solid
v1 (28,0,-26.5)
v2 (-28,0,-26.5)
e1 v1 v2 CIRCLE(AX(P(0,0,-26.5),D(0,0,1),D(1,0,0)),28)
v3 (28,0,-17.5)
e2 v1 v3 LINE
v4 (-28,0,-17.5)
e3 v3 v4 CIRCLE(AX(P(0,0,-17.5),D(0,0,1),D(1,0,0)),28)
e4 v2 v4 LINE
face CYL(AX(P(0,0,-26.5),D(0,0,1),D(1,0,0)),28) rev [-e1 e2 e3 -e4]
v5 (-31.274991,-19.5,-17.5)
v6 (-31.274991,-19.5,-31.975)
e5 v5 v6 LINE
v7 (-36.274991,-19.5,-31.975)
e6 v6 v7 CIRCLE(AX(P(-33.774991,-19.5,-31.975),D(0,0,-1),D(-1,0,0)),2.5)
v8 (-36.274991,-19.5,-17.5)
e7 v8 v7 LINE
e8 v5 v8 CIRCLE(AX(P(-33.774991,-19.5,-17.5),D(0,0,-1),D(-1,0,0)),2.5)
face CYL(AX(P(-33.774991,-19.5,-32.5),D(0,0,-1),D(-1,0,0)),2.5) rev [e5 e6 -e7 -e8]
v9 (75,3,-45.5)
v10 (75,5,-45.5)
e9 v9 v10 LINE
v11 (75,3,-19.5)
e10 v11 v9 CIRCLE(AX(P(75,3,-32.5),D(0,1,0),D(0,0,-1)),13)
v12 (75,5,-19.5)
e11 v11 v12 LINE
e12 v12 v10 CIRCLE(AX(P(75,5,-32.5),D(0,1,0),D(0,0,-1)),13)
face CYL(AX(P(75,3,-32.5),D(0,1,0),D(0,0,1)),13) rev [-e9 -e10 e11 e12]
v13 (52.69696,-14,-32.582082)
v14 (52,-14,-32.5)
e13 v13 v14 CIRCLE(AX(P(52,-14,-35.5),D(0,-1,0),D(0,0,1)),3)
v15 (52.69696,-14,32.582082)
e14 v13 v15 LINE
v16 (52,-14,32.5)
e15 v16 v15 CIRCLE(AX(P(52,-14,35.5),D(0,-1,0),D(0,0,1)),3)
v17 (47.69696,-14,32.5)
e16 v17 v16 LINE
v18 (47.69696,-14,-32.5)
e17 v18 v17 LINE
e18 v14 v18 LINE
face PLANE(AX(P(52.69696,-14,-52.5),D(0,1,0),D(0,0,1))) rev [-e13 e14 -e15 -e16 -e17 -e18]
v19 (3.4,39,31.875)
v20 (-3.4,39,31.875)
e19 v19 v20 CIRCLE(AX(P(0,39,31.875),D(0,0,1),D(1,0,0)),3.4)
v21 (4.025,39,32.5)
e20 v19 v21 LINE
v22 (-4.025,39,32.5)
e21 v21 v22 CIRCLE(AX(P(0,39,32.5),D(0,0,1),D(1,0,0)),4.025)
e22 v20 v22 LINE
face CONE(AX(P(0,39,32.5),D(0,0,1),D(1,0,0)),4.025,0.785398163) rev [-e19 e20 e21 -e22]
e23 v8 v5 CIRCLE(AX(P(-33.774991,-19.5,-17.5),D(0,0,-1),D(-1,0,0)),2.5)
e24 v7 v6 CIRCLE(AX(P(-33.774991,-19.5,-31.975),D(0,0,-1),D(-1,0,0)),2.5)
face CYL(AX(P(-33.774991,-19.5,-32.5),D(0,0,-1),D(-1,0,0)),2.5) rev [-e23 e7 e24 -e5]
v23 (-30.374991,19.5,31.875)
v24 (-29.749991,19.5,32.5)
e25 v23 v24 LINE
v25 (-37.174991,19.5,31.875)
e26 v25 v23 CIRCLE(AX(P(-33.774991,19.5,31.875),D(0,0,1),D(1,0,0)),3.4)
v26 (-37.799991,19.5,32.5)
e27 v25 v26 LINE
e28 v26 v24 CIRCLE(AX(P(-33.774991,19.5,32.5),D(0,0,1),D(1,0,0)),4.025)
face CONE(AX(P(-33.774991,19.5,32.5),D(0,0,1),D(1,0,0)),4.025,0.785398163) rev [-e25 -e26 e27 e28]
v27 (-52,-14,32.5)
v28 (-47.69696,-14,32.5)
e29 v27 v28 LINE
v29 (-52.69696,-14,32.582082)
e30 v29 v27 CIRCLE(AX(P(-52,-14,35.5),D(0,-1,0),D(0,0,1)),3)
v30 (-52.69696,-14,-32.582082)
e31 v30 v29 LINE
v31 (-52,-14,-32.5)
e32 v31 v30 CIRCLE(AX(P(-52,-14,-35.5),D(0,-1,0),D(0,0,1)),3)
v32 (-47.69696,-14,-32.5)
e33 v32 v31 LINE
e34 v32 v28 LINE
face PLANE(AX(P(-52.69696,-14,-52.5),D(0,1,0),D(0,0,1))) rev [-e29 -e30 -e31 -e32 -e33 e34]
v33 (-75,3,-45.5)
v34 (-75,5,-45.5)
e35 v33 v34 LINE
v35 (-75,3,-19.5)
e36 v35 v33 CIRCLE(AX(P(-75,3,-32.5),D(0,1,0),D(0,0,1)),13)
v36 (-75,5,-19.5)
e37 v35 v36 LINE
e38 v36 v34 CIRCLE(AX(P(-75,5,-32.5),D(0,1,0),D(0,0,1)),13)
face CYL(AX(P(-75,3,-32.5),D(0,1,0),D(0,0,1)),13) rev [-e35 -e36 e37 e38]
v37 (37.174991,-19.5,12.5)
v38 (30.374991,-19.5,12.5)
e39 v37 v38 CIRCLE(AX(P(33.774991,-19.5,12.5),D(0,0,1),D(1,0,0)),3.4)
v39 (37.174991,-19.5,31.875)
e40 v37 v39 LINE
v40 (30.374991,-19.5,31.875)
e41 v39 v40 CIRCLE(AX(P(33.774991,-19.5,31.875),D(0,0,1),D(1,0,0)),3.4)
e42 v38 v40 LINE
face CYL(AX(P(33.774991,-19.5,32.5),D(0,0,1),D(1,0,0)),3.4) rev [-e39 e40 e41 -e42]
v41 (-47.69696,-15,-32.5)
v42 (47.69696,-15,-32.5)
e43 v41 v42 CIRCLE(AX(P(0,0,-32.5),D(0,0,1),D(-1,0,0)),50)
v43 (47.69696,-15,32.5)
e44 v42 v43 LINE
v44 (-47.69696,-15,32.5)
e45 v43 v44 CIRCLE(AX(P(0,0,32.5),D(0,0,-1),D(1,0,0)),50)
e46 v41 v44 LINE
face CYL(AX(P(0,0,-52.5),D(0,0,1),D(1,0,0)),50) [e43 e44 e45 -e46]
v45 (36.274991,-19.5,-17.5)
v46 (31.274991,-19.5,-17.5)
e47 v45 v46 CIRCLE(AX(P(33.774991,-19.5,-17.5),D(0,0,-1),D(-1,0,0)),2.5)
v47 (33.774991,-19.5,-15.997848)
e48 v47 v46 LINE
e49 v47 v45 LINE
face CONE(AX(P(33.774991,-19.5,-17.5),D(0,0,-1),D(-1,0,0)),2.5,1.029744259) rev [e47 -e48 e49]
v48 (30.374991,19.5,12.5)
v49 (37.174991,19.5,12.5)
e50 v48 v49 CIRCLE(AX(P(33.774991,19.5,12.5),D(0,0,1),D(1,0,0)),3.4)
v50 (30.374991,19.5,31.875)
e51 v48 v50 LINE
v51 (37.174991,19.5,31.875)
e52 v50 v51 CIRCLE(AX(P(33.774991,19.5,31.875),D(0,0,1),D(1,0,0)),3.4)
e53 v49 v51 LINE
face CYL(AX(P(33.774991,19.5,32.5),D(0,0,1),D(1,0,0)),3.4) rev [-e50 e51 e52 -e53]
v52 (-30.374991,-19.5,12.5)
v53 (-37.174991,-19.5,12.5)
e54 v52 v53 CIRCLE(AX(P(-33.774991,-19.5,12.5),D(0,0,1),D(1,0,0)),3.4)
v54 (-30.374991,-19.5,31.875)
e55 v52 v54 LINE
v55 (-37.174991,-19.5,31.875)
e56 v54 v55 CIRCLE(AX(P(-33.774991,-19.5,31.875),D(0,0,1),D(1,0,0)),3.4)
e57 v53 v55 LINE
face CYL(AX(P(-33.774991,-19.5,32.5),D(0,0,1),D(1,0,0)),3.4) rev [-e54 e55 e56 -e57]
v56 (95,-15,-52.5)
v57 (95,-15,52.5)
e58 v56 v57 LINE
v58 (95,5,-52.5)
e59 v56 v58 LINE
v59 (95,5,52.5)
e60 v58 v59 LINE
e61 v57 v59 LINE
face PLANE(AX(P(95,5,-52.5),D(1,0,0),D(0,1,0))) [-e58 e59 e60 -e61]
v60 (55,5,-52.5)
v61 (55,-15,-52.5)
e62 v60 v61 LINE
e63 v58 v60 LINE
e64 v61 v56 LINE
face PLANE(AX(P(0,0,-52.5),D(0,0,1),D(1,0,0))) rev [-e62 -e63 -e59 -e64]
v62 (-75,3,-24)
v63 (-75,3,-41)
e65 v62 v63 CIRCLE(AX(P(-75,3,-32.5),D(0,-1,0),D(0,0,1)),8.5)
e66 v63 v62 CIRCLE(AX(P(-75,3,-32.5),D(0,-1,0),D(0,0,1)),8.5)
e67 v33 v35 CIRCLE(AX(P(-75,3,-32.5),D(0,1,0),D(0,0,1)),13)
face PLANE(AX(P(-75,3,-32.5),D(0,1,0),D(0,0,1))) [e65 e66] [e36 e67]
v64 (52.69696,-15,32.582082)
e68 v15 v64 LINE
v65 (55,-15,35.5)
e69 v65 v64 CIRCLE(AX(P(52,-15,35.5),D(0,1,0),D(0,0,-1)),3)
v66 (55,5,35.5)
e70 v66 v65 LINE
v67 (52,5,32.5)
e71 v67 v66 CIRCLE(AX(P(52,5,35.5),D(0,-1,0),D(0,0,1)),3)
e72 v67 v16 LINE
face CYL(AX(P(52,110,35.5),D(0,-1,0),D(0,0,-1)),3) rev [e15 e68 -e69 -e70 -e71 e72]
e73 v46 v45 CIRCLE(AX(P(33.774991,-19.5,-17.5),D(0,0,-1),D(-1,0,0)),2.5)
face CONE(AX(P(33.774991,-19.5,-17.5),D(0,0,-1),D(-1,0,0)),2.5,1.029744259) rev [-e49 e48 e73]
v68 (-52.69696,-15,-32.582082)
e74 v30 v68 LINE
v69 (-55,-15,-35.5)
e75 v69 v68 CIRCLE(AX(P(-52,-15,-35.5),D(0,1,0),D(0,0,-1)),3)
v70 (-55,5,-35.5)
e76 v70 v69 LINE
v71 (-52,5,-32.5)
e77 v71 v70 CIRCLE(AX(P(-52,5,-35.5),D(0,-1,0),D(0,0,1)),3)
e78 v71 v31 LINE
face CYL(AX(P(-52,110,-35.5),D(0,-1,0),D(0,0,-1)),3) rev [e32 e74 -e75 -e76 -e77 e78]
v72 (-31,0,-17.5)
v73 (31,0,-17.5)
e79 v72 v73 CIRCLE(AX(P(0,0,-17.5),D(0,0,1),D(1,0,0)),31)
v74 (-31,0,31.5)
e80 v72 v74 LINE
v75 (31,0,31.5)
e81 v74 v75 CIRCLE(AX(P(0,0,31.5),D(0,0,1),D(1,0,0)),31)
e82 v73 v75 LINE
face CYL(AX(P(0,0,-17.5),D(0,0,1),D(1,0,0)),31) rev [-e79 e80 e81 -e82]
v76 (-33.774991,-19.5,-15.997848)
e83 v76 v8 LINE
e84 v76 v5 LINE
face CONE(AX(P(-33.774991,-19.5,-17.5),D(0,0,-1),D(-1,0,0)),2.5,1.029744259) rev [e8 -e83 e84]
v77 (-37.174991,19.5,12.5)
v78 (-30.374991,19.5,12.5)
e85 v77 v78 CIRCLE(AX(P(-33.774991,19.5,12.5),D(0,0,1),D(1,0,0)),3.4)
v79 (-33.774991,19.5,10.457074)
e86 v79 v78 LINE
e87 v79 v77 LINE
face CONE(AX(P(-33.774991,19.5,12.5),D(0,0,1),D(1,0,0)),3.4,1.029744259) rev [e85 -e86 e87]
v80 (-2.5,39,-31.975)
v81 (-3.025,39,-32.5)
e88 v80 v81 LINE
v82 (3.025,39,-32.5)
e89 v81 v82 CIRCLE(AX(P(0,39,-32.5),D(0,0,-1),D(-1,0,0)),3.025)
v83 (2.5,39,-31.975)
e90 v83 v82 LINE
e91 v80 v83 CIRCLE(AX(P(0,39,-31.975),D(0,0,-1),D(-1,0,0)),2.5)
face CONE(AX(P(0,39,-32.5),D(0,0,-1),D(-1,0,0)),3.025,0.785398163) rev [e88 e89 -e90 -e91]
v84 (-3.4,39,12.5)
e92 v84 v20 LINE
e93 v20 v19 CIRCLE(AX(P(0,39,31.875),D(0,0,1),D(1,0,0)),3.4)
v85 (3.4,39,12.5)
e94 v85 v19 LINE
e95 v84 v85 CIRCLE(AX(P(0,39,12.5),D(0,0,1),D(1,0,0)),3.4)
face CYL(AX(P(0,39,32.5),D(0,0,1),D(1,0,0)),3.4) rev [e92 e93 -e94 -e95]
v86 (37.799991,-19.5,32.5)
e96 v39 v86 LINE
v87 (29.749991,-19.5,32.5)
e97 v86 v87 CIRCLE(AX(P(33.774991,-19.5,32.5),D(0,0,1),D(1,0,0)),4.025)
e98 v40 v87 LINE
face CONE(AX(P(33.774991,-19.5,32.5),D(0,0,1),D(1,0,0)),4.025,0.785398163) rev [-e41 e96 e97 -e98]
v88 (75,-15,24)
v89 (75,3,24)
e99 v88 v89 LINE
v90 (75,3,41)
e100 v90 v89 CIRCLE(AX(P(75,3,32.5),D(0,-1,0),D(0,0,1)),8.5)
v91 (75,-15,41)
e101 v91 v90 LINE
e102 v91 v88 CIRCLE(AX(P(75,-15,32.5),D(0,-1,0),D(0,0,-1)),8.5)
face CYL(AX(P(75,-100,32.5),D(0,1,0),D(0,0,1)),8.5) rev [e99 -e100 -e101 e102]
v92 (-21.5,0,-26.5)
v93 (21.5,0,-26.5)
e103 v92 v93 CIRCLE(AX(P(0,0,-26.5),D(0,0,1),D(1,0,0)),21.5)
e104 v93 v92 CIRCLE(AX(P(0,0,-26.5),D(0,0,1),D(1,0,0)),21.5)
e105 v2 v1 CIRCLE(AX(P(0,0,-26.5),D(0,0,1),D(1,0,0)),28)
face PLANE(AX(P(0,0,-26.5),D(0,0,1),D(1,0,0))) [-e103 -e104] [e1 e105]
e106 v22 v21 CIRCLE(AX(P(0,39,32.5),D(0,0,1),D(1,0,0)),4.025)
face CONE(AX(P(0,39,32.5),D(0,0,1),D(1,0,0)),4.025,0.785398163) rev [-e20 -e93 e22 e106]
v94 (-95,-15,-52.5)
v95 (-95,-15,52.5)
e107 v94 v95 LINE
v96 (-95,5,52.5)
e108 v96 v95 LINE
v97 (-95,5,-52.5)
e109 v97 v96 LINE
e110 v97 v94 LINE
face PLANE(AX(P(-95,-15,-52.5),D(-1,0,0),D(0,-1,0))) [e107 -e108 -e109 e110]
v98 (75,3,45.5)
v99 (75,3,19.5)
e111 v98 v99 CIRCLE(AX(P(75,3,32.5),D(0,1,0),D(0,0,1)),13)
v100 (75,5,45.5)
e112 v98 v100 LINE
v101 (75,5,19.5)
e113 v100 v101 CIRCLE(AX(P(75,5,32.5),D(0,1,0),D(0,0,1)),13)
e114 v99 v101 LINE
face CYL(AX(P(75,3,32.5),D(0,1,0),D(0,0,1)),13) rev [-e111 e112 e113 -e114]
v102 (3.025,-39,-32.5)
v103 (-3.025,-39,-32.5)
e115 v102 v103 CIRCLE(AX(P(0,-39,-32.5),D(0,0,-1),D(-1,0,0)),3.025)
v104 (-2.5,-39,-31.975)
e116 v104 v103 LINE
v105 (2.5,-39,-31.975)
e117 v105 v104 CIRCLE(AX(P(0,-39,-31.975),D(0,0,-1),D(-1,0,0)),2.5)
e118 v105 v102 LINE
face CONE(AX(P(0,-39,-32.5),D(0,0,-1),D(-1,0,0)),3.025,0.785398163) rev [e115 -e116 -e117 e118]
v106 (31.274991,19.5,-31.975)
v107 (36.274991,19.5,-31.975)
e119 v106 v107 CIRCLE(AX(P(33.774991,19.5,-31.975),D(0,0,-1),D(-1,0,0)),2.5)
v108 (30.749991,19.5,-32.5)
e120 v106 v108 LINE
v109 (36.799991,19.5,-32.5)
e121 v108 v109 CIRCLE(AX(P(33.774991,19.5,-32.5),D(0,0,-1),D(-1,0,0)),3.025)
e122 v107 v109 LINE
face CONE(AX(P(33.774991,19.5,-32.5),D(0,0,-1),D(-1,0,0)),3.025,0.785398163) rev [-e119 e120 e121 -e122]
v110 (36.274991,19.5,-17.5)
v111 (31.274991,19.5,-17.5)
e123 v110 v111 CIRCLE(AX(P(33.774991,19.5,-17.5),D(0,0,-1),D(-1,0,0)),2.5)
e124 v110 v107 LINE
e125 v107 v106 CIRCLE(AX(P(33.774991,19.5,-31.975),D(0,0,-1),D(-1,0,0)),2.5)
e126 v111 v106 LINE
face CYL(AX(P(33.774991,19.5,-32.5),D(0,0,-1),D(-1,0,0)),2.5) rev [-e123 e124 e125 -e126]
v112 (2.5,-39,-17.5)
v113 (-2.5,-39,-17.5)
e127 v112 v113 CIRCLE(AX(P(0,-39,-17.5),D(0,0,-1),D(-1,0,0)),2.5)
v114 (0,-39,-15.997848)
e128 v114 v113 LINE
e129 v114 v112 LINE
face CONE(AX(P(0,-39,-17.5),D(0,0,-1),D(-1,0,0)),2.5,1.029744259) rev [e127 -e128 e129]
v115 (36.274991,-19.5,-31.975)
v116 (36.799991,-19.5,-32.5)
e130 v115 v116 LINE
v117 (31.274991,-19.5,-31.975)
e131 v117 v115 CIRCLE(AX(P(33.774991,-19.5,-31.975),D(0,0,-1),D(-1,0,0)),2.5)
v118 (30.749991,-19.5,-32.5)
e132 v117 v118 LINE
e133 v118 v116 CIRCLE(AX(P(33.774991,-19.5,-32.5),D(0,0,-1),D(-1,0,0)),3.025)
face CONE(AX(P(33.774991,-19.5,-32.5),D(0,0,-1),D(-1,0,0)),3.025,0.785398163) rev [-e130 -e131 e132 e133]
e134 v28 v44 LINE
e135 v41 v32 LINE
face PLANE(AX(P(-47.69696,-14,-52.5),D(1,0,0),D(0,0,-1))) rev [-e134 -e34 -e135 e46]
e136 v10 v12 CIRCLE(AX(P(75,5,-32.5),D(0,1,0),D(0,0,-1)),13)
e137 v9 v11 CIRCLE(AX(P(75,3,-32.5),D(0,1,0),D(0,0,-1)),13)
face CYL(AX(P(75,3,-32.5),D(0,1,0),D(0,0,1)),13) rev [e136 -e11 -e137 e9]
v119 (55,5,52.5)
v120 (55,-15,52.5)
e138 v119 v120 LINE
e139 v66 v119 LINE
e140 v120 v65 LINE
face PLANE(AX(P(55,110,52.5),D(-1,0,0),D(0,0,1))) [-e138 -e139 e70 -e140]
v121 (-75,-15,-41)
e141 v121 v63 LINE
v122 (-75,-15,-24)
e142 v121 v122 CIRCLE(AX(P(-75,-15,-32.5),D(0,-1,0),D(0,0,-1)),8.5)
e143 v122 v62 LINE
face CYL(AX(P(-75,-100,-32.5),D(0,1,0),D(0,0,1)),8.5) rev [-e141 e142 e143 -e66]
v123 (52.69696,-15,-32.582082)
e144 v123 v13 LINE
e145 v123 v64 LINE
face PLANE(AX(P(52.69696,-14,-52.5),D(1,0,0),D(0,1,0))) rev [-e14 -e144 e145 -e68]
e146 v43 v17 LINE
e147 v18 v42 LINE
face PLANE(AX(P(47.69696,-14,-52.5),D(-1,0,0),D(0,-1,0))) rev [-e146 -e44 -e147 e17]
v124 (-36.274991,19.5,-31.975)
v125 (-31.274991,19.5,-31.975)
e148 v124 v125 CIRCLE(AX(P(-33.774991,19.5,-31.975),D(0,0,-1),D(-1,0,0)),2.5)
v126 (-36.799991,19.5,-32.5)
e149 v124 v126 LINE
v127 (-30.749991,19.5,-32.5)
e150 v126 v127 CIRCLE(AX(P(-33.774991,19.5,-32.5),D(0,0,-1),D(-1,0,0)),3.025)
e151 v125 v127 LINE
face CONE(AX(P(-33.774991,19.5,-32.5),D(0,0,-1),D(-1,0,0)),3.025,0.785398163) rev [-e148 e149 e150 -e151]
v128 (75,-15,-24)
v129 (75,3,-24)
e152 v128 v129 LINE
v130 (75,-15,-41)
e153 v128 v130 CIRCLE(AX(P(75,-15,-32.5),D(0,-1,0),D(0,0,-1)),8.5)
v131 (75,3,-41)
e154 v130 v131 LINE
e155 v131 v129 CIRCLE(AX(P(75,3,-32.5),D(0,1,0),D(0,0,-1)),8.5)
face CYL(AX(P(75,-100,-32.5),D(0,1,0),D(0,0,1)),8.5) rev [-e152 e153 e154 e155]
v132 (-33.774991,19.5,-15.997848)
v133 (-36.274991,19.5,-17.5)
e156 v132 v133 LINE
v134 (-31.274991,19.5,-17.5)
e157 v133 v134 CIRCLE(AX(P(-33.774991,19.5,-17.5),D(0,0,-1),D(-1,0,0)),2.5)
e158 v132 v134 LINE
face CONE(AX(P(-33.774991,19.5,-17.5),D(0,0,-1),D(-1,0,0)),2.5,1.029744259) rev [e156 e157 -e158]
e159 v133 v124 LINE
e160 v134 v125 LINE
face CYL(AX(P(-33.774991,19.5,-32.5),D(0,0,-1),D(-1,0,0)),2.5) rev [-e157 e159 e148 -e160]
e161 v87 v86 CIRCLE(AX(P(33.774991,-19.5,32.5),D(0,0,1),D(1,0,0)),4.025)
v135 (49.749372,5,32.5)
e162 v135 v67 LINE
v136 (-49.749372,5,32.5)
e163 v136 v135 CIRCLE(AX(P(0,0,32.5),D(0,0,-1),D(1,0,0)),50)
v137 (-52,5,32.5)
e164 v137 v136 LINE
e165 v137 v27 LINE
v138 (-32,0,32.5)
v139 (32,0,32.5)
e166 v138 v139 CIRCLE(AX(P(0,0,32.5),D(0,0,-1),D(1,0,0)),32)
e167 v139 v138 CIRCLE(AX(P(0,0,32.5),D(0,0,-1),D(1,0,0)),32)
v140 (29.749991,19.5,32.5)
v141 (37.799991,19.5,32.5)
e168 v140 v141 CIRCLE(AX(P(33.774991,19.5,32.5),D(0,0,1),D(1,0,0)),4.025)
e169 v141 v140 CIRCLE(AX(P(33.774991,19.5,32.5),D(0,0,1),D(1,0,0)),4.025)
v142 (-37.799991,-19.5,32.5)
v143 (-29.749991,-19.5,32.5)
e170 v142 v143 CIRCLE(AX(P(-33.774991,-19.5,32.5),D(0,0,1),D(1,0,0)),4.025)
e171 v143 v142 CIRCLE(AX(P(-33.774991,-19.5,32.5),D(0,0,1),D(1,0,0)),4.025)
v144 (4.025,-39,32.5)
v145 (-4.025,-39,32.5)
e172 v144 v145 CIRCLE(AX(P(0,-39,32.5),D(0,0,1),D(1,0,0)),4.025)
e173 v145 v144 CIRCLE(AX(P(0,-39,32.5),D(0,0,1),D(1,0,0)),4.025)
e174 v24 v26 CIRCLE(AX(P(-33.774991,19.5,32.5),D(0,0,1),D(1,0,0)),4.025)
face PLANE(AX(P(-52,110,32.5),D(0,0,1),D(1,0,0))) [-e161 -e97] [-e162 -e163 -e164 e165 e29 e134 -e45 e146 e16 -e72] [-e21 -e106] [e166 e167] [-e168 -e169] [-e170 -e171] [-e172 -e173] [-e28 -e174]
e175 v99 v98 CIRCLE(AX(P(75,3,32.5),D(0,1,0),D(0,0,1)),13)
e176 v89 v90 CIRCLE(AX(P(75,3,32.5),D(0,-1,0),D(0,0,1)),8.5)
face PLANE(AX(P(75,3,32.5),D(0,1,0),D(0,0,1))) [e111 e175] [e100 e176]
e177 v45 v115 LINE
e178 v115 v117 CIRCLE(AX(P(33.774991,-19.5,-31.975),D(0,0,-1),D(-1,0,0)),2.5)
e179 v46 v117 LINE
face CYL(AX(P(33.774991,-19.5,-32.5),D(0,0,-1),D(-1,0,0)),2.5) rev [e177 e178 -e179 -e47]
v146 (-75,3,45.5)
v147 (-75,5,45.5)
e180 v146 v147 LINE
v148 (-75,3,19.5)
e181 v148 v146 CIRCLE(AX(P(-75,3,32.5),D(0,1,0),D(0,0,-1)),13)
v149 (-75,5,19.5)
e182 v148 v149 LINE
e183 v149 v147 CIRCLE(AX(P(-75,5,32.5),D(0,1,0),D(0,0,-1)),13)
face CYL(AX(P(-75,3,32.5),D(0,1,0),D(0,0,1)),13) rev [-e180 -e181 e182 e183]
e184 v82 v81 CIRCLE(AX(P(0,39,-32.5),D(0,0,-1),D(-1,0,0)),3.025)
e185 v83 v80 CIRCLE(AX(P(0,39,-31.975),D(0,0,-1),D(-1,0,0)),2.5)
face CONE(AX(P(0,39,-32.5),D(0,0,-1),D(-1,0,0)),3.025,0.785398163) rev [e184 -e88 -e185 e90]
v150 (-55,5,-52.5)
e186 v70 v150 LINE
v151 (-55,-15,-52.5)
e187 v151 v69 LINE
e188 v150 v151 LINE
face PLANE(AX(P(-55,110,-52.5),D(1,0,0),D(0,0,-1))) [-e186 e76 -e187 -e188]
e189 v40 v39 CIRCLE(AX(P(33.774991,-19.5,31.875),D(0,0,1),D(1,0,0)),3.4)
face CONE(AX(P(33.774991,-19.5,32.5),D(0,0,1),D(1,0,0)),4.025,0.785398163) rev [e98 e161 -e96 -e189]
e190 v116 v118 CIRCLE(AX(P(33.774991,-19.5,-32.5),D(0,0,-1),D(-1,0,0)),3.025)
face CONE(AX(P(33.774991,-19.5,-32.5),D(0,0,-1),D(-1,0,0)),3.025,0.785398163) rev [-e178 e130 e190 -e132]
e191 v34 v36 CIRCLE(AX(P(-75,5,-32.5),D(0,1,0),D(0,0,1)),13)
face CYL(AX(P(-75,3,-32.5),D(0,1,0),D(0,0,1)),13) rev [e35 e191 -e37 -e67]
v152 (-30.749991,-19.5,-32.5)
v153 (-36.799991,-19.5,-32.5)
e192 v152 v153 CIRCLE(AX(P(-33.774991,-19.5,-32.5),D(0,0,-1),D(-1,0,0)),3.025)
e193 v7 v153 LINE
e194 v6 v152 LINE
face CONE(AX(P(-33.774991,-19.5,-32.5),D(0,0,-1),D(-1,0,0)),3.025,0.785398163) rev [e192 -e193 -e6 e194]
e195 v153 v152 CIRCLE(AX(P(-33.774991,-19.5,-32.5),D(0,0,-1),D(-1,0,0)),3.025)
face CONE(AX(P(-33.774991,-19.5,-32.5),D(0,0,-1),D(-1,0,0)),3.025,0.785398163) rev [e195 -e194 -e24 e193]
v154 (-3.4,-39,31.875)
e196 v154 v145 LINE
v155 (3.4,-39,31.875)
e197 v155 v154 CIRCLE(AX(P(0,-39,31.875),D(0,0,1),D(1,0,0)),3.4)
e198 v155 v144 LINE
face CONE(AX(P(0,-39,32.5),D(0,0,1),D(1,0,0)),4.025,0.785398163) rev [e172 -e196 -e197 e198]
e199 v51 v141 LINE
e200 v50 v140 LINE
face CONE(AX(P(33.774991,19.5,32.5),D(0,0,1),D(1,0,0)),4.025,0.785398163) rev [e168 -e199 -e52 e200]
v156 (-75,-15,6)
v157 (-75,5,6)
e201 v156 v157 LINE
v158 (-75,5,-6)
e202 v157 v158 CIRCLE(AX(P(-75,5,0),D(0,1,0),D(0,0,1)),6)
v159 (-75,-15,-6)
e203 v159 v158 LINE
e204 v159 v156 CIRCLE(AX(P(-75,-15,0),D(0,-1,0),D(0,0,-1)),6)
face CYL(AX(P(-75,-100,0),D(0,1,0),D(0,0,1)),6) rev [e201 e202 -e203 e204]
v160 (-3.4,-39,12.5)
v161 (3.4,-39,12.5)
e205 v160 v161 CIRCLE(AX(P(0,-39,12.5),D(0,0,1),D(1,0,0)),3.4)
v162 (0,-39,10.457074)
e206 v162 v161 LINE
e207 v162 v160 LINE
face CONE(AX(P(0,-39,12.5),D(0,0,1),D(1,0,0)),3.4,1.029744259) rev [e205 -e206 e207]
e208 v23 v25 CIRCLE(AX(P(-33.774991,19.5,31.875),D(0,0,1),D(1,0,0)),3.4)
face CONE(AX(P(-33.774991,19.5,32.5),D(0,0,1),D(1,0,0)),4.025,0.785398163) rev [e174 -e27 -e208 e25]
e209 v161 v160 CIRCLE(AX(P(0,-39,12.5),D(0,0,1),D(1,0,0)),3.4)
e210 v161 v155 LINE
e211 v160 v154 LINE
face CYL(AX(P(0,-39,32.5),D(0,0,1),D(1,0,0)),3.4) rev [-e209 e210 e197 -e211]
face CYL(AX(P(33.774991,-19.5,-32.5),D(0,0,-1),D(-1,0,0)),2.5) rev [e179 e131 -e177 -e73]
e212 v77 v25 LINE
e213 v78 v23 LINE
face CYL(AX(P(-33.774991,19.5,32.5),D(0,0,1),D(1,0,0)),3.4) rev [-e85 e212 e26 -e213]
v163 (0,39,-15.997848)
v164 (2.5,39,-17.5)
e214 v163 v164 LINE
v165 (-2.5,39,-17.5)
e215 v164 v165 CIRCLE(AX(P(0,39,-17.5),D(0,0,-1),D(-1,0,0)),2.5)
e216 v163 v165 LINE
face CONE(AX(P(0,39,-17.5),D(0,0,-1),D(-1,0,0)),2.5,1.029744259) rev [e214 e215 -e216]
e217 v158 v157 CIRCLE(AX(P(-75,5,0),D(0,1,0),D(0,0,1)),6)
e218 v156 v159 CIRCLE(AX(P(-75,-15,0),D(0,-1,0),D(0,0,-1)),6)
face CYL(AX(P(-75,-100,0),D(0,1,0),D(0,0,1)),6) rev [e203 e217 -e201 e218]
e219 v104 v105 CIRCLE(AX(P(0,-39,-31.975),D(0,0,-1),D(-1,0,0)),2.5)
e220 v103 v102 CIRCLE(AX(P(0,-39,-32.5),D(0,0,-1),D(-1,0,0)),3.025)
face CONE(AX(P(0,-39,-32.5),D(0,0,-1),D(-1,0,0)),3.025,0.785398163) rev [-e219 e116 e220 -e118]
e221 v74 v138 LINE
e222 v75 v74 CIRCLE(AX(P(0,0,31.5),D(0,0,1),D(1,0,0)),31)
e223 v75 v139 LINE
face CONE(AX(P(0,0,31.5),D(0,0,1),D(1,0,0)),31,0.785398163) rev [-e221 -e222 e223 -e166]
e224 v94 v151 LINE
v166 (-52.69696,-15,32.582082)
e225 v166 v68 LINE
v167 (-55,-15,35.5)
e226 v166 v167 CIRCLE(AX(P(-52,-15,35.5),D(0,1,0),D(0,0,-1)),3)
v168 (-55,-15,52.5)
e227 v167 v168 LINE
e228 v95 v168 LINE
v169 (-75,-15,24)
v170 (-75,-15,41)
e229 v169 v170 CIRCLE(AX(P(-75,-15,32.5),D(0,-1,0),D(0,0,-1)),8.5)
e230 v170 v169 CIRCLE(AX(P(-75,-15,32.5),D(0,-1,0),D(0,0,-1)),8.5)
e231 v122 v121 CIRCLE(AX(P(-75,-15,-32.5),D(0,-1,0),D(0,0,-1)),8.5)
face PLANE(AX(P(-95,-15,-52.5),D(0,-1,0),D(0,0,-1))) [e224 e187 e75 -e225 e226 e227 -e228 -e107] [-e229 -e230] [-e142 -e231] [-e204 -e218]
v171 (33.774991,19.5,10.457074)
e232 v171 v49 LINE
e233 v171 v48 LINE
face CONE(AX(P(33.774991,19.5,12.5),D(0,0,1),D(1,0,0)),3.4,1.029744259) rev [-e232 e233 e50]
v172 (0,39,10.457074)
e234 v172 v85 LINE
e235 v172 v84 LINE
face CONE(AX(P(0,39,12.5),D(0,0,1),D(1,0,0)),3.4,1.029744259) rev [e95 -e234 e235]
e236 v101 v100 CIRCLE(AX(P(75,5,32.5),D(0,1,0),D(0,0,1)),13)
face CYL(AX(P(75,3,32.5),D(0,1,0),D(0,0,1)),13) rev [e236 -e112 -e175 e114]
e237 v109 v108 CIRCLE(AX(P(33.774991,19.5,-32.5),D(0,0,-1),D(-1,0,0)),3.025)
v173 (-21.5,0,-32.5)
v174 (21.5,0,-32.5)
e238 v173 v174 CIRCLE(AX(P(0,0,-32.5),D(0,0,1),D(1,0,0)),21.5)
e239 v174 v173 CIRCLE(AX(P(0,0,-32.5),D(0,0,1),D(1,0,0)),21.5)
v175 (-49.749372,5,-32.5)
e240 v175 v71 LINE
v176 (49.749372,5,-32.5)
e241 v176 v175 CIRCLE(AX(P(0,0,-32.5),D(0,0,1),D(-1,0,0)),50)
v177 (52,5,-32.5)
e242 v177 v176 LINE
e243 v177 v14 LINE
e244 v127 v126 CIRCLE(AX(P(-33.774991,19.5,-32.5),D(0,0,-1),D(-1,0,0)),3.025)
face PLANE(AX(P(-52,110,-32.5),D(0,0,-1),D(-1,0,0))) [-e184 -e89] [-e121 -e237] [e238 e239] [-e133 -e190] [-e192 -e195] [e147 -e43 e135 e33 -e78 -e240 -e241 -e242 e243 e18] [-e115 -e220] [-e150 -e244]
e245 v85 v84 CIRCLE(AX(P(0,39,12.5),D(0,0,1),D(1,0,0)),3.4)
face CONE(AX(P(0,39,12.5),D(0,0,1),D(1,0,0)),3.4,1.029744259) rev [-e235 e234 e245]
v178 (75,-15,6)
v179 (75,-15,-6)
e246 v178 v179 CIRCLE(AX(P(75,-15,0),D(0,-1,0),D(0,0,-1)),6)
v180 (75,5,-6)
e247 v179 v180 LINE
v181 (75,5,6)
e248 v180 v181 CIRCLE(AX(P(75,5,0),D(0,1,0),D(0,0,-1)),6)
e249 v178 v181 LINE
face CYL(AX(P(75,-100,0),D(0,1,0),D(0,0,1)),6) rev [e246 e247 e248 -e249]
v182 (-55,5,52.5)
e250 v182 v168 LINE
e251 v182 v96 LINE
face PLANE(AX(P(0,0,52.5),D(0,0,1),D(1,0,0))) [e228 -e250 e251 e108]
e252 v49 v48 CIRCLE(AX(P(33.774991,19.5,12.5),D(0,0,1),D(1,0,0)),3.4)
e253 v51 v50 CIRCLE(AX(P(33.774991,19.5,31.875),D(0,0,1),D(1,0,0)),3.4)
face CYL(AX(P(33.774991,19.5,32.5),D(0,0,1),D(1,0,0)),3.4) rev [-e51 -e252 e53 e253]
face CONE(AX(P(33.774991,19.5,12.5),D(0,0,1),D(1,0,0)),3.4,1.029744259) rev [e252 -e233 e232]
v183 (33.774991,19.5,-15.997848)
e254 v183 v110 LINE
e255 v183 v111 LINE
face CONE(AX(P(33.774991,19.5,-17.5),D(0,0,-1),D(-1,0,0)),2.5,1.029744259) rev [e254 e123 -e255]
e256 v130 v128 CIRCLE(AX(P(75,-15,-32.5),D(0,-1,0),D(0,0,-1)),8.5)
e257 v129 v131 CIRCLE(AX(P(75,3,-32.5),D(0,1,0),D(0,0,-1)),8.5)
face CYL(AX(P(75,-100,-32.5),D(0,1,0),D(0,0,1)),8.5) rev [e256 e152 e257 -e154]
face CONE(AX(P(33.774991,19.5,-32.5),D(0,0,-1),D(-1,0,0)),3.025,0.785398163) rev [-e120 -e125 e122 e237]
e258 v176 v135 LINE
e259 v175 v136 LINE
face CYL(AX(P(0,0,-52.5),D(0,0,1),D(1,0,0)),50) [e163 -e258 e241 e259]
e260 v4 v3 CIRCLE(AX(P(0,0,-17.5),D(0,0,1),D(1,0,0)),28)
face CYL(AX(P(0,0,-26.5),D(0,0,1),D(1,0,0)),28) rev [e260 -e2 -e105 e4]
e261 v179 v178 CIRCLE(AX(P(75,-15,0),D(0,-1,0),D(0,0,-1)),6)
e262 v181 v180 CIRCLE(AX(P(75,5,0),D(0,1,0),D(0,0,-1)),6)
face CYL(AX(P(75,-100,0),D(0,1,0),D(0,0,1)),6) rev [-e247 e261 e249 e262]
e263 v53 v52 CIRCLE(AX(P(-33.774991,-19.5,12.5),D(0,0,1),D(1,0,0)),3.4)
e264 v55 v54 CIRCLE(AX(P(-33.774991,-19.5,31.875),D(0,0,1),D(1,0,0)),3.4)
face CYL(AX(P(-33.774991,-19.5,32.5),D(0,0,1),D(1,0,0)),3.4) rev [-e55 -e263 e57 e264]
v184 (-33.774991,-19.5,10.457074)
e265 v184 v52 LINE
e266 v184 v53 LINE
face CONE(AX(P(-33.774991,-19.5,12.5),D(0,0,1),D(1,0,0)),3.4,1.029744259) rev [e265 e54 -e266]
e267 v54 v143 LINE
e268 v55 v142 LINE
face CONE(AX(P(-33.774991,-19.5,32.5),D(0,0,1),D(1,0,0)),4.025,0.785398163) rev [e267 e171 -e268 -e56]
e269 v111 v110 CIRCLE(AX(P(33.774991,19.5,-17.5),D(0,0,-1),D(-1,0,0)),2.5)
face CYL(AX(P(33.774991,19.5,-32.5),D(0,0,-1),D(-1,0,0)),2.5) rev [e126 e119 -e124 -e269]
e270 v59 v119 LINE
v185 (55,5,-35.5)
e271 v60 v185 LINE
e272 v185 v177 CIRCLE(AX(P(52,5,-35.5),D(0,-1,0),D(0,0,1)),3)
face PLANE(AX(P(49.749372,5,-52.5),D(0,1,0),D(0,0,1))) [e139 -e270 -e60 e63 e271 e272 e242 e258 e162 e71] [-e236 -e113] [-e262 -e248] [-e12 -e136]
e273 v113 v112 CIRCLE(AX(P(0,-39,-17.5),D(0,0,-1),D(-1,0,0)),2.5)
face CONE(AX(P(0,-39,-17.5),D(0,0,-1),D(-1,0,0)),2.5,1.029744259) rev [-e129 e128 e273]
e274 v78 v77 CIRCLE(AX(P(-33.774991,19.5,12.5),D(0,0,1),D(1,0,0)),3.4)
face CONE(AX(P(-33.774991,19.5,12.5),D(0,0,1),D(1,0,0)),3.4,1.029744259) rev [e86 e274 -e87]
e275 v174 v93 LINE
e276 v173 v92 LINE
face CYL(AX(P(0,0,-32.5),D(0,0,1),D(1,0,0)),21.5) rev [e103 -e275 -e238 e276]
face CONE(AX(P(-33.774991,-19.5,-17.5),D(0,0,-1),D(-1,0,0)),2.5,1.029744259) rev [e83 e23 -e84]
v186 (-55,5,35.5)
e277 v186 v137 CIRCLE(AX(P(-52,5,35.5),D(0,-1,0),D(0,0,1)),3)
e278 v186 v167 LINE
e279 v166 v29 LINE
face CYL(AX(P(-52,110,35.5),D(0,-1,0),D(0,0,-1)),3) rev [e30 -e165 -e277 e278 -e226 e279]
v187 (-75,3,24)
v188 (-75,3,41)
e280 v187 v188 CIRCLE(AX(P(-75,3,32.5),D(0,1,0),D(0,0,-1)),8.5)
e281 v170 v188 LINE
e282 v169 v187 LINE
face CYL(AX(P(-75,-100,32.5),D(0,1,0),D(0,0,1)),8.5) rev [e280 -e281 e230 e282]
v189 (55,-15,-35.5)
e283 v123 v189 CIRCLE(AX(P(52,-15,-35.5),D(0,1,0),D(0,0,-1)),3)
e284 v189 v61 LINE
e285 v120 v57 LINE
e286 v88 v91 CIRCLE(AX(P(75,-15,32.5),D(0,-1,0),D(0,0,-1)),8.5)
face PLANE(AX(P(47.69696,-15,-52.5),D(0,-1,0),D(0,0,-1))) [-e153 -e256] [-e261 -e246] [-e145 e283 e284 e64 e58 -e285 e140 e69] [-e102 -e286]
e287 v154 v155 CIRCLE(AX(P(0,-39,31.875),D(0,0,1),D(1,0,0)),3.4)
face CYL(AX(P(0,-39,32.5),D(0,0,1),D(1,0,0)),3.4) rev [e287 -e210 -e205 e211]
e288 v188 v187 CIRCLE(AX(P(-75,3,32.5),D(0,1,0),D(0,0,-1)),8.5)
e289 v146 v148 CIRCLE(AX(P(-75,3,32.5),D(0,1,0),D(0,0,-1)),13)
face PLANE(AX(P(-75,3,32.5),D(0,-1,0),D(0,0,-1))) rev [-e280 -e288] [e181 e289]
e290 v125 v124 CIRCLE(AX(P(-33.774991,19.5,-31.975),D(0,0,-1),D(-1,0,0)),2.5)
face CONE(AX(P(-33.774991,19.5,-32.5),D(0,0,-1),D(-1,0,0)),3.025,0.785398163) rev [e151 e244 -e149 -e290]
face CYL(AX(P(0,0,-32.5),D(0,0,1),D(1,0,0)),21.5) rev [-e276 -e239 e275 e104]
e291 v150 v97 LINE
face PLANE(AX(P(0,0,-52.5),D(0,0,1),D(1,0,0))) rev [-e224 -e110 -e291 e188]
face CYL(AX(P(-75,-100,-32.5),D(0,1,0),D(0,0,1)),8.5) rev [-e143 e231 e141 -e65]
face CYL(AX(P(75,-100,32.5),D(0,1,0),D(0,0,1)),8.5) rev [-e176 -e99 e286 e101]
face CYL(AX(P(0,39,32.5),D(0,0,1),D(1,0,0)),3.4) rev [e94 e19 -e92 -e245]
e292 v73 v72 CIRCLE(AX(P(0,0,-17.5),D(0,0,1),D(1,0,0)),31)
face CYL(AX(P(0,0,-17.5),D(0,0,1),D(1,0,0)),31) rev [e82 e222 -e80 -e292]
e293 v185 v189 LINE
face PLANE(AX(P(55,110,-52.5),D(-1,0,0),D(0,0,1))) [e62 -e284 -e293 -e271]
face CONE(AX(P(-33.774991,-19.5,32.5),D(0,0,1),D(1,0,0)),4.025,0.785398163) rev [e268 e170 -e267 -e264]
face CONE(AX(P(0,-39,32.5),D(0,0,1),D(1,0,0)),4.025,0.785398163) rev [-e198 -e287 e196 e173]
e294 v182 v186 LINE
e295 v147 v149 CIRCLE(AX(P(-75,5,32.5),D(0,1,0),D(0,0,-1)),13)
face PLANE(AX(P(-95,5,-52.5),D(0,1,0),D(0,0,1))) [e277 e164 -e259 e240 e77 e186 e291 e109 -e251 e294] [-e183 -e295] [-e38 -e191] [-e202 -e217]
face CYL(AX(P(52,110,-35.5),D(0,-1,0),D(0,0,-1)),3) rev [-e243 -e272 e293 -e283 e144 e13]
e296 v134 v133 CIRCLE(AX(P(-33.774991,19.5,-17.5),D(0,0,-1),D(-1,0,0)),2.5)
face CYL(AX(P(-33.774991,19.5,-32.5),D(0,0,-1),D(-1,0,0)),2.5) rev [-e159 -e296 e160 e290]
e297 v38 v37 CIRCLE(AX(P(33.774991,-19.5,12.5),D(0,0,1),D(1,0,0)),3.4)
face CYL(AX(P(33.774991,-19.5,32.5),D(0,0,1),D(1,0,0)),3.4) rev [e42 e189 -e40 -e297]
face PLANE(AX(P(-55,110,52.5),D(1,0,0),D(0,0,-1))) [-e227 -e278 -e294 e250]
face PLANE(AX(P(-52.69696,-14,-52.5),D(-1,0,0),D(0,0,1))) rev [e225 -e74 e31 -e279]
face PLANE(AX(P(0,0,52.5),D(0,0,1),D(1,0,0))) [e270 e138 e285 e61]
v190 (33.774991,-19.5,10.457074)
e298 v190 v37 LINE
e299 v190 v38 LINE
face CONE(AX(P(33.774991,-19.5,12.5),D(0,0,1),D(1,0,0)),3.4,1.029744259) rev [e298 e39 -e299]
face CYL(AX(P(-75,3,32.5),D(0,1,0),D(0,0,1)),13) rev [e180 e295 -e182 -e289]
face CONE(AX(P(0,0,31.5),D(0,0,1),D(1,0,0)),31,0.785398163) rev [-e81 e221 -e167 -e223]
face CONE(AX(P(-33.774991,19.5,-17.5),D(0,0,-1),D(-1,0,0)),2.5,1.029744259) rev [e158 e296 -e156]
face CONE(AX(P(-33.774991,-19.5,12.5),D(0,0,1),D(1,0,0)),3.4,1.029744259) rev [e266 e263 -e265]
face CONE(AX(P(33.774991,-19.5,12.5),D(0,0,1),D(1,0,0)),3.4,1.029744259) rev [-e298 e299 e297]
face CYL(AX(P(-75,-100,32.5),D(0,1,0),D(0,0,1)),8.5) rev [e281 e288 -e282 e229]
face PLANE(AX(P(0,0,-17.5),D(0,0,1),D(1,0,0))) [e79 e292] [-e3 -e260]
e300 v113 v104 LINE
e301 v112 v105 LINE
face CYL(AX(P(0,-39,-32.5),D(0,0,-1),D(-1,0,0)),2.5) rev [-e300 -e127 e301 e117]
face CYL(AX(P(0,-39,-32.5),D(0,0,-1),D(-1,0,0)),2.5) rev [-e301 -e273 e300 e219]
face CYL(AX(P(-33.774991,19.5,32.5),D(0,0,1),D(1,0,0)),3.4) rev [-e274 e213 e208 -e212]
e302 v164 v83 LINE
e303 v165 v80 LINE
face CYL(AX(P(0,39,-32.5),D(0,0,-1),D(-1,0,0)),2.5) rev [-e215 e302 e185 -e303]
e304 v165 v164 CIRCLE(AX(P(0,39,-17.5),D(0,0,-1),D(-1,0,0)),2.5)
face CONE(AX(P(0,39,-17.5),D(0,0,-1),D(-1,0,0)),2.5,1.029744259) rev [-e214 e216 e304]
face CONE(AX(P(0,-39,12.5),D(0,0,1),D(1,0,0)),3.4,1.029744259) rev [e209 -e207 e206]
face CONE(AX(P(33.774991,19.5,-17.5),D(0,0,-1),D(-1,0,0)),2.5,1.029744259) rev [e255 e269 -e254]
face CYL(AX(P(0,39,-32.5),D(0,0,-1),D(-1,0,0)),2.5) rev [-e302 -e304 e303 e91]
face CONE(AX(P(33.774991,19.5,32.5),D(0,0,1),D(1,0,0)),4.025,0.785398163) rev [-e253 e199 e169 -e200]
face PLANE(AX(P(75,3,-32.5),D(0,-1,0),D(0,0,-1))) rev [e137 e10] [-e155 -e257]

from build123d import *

# Parameters (mm, degrees)
BOSS_EXTRUDE1_DEPTH         = 52.5
BOSS_EXTRUDE1_DEPTH_BACK    = 52.5
SKETCH3_W                   = 5
SKETCH3_H                   = 10
CUT_EXTRUDE1_DEPTH          = 105
CUT_EXTRUDE2_DEPTH          = 105
CUT_EXTRUDE2_DEPTH_BACK     = 105
SKETCH5_R                   = 8.5
SKETCH5_R_2                 = 6
CUT_EXTRUDE3_DEPTH          = 105
SKETCH6_R                   = 13
CUT_EXTRUDE4_DEPTH          = 2
SKETCH7_R                   = 31
CUT_EXTRUDE5_DEPTH          = 50
SKETCH8_R                   = 28
CUT_EXTRUDE6_DEPTH          = 59
SKETCH9_R                   = 21.5
CUT_EXTRUDE7_DEPTH          = 65
CHAMFER1_SIZE               = 1
M8_TAPPED_HOLE3_D           = 6.8
M8_TAPPED_HOLE3_DEPTH       = 20
M8_TAPPED_HOLE3_CSINK_D     = 8.05
M8_TAPPED_HOLE3_CSINK_ANGLE = 90
M8_TAPPED_HOLE3_TIP         = 2.042926105
M6_TAPPED_HOLE1_D           = 5
M6_TAPPED_HOLE1_DEPTH       = 15
M6_TAPPED_HOLE1_CSINK_D     = 6.05
M6_TAPPED_HOLE1_CSINK_ANGLE = 90
M6_TAPPED_HOLE1_TIP         = 1.502151548


with BuildPart() as part:
    # Sketch1 → Boss-Extrude1 (new, two sides: drawn at the far end of the back side and taken through both)
    with BuildSketch(Plane.XY.offset(-BOSS_EXTRUDE1_DEPTH_BACK)):
        with BuildLine():
            Line((-95, -15), (-47.696960071, -15))
            ThreePointArc((-47.696960071, -15), (0, -50), (47.696960071, -15))
            Line((47.696960071, -15), (95, -15))
            Line((95, -15), (95, 5))
            Line((95, 5), (49.749371855, 5))
            ThreePointArc((49.749371855, 5), (0, 50), (-49.749371855, 5))
            Line((-49.749371855, 5), (-95, 5))
            Line((-95, 5), (-95, -15))
        make_face()
    extrude(amount=BOSS_EXTRUDE1_DEPTH + BOSS_EXTRUDE1_DEPTH_BACK)

    # Sketch3 → Cut-Extrude1 (cut)
    with BuildSketch(Plane.XY.offset(52.5)):
        with Locations((50.196960071, -19)):
            Rectangle(SKETCH3_W, SKETCH3_H)
        with Locations((-50.196960071, -19)):
            Rectangle(SKETCH3_W, SKETCH3_H)
    extrude(amount=-CUT_EXTRUDE1_DEPTH, mode=Mode.SUBTRACT)

    # Sketch4 → Cut-Extrude2 (cut, two sides: drawn at the far end of the back side and taken through both)
    with BuildSketch(Plane(origin=(0, 5, 0), x_dir=(1, 0, 0), z_dir=(0, 1, 0)).offset(-CUT_EXTRUDE2_DEPTH_BACK)):
        with BuildLine():
            Line((-52, -32.5), (52, -32.5))
            ThreePointArc((52, -32.5), (54.121320344, -33.378679656), (55, -35.5))
            Line((55, -35.5), (55, -52.5))
            Line((55, -52.5), (-55, -52.5))
            Line((-55, -52.5), (-55, -35.5))
            ThreePointArc((-55, -35.5), (-54.121320344, -33.378679656), (-52, -32.5))
        make_face()
        with BuildLine():
            Line((-55, 52.5), (55, 52.5))
            Line((55, 52.5), (55, 35.5))
            ThreePointArc((55, 35.5), (54.121320344, 33.378679656), (52, 32.5))
            Line((52, 32.5), (-52, 32.5))
            ThreePointArc((-52, 32.5), (-54.121320344, 33.378679656), (-55, 35.5))
            Line((-55, 35.5), (-55, 52.5))
        make_face()
    extrude(amount=CUT_EXTRUDE2_DEPTH + CUT_EXTRUDE2_DEPTH_BACK, mode=Mode.SUBTRACT)

    # Sketch5 → Cut-Extrude3 (cut)
    with BuildSketch(Plane(origin=(0, 5, 0), x_dir=(1, 0, 0), z_dir=(0, 1, 0))):
        with Locations(Location((-75, 32.5, 0), (0, 0, 270))):
            Circle(SKETCH5_R)
        with Locations(Location((-75, -32.5, 0), (0, 0, 90))):
            Circle(SKETCH5_R)
        with Locations(Location((75, -32.5, 0), (0, 0, 270))):
            Circle(SKETCH5_R)
        with Locations(Location((75, 32.5, 0), (0, 0, 90))):
            Circle(SKETCH5_R)
        with Locations(Location((-75, 0, 0), (0, 0, 270))):
            Circle(SKETCH5_R_2)
        with Locations(Location((75, 0, 0), (0, 0, 90))):
            Circle(SKETCH5_R_2)
    extrude(amount=-CUT_EXTRUDE3_DEPTH, mode=Mode.SUBTRACT)

    # Sketch6 → Cut-Extrude4 (cut)
    with BuildSketch(Plane(origin=(0, 5, 0), x_dir=(1, 0, 0), z_dir=(0, 1, 0))):
        with Locations(Location((-75, 32.5, 0), (0, 0, 270))):
            Circle(SKETCH6_R)
        with Locations(Location((75, 32.5, 0), (0, 0, 90))):
            Circle(SKETCH6_R)
        with Locations(Location((75, -32.5, 0), (0, 0, 270))):
            Circle(SKETCH6_R)
        with Locations(Location((-75, -32.5, 0), (0, 0, 90))):
            Circle(SKETCH6_R)
    extrude(amount=-CUT_EXTRUDE4_DEPTH, mode=Mode.SUBTRACT)

    # Sketch7 → Cut-Extrude5 (cut)
    with BuildSketch(Plane.XY.offset(32.5)):
        Circle(SKETCH7_R)
    extrude(amount=-CUT_EXTRUDE5_DEPTH, mode=Mode.SUBTRACT)

    # Sketch8 → Cut-Extrude6 (cut)
    with BuildSketch(Plane.XY.offset(32.5)):
        Circle(SKETCH8_R)
    extrude(amount=-CUT_EXTRUDE6_DEPTH, mode=Mode.SUBTRACT)

    # Sketch9 → Cut-Extrude7 (cut)
    with BuildSketch(Plane.XY.offset(32.5)):
        Circle(SKETCH9_R)
    extrude(amount=-CUT_EXTRUDE7_DEPTH, mode=Mode.SUBTRACT)

    # Chamfer1
    chamfer1_edges = [part.edges().sort_by_distance(p)[0] for p in [
        (-31, 0, 32.5),
    ]]
    chamfer(chamfer1_edges, length=CHAMFER1_SIZE)

    # M8 Tapped Hole3
    with Locations(Plane.XY.offset(32.5)):
        with Locations((-33.774990748, 19.5), (0, 39), (33.774990748, 19.5), (33.774990748, -19.5), (0, -39), (-33.774990748, -19.5), (0, 0)):
            CounterSinkHole(M8_TAPPED_HOLE3_D / 2, M8_TAPPED_HOLE3_CSINK_D / 2, depth=M8_TAPPED_HOLE3_DEPTH, counter_sink_angle=M8_TAPPED_HOLE3_CSINK_ANGLE)
            with Locations((0, 0, -(M8_TAPPED_HOLE3_DEPTH + M8_TAPPED_HOLE3_TIP / 2))):  # 118° drill point
                Cone(0, M8_TAPPED_HOLE3_D / 2, M8_TAPPED_HOLE3_TIP, mode=Mode.SUBTRACT)

    # M6 Tapped Hole1
    with Locations(Plane(origin=(0, 0, -32.5), x_dir=(-1, 0, 0), z_dir=(0, 0, -1))):
        with Locations((0, 0), (0, 39), (33.774990748, 19.5), (33.774990748, -19.5), (0, -39), (-33.774990748, -19.5), (-33.774990748, 19.5)):
            CounterSinkHole(M6_TAPPED_HOLE1_D / 2, M6_TAPPED_HOLE1_CSINK_D / 2, depth=M6_TAPPED_HOLE1_DEPTH, counter_sink_angle=M6_TAPPED_HOLE1_CSINK_ANGLE)
            with Locations((0, 0, -(M6_TAPPED_HOLE1_DEPTH + M6_TAPPED_HOLE1_TIP / 2))):  # 118° drill point
                Cone(0, M6_TAPPED_HOLE1_D / 2, M6_TAPPED_HOLE1_TIP, mode=Mode.SUBTRACT)


solid = part.part
